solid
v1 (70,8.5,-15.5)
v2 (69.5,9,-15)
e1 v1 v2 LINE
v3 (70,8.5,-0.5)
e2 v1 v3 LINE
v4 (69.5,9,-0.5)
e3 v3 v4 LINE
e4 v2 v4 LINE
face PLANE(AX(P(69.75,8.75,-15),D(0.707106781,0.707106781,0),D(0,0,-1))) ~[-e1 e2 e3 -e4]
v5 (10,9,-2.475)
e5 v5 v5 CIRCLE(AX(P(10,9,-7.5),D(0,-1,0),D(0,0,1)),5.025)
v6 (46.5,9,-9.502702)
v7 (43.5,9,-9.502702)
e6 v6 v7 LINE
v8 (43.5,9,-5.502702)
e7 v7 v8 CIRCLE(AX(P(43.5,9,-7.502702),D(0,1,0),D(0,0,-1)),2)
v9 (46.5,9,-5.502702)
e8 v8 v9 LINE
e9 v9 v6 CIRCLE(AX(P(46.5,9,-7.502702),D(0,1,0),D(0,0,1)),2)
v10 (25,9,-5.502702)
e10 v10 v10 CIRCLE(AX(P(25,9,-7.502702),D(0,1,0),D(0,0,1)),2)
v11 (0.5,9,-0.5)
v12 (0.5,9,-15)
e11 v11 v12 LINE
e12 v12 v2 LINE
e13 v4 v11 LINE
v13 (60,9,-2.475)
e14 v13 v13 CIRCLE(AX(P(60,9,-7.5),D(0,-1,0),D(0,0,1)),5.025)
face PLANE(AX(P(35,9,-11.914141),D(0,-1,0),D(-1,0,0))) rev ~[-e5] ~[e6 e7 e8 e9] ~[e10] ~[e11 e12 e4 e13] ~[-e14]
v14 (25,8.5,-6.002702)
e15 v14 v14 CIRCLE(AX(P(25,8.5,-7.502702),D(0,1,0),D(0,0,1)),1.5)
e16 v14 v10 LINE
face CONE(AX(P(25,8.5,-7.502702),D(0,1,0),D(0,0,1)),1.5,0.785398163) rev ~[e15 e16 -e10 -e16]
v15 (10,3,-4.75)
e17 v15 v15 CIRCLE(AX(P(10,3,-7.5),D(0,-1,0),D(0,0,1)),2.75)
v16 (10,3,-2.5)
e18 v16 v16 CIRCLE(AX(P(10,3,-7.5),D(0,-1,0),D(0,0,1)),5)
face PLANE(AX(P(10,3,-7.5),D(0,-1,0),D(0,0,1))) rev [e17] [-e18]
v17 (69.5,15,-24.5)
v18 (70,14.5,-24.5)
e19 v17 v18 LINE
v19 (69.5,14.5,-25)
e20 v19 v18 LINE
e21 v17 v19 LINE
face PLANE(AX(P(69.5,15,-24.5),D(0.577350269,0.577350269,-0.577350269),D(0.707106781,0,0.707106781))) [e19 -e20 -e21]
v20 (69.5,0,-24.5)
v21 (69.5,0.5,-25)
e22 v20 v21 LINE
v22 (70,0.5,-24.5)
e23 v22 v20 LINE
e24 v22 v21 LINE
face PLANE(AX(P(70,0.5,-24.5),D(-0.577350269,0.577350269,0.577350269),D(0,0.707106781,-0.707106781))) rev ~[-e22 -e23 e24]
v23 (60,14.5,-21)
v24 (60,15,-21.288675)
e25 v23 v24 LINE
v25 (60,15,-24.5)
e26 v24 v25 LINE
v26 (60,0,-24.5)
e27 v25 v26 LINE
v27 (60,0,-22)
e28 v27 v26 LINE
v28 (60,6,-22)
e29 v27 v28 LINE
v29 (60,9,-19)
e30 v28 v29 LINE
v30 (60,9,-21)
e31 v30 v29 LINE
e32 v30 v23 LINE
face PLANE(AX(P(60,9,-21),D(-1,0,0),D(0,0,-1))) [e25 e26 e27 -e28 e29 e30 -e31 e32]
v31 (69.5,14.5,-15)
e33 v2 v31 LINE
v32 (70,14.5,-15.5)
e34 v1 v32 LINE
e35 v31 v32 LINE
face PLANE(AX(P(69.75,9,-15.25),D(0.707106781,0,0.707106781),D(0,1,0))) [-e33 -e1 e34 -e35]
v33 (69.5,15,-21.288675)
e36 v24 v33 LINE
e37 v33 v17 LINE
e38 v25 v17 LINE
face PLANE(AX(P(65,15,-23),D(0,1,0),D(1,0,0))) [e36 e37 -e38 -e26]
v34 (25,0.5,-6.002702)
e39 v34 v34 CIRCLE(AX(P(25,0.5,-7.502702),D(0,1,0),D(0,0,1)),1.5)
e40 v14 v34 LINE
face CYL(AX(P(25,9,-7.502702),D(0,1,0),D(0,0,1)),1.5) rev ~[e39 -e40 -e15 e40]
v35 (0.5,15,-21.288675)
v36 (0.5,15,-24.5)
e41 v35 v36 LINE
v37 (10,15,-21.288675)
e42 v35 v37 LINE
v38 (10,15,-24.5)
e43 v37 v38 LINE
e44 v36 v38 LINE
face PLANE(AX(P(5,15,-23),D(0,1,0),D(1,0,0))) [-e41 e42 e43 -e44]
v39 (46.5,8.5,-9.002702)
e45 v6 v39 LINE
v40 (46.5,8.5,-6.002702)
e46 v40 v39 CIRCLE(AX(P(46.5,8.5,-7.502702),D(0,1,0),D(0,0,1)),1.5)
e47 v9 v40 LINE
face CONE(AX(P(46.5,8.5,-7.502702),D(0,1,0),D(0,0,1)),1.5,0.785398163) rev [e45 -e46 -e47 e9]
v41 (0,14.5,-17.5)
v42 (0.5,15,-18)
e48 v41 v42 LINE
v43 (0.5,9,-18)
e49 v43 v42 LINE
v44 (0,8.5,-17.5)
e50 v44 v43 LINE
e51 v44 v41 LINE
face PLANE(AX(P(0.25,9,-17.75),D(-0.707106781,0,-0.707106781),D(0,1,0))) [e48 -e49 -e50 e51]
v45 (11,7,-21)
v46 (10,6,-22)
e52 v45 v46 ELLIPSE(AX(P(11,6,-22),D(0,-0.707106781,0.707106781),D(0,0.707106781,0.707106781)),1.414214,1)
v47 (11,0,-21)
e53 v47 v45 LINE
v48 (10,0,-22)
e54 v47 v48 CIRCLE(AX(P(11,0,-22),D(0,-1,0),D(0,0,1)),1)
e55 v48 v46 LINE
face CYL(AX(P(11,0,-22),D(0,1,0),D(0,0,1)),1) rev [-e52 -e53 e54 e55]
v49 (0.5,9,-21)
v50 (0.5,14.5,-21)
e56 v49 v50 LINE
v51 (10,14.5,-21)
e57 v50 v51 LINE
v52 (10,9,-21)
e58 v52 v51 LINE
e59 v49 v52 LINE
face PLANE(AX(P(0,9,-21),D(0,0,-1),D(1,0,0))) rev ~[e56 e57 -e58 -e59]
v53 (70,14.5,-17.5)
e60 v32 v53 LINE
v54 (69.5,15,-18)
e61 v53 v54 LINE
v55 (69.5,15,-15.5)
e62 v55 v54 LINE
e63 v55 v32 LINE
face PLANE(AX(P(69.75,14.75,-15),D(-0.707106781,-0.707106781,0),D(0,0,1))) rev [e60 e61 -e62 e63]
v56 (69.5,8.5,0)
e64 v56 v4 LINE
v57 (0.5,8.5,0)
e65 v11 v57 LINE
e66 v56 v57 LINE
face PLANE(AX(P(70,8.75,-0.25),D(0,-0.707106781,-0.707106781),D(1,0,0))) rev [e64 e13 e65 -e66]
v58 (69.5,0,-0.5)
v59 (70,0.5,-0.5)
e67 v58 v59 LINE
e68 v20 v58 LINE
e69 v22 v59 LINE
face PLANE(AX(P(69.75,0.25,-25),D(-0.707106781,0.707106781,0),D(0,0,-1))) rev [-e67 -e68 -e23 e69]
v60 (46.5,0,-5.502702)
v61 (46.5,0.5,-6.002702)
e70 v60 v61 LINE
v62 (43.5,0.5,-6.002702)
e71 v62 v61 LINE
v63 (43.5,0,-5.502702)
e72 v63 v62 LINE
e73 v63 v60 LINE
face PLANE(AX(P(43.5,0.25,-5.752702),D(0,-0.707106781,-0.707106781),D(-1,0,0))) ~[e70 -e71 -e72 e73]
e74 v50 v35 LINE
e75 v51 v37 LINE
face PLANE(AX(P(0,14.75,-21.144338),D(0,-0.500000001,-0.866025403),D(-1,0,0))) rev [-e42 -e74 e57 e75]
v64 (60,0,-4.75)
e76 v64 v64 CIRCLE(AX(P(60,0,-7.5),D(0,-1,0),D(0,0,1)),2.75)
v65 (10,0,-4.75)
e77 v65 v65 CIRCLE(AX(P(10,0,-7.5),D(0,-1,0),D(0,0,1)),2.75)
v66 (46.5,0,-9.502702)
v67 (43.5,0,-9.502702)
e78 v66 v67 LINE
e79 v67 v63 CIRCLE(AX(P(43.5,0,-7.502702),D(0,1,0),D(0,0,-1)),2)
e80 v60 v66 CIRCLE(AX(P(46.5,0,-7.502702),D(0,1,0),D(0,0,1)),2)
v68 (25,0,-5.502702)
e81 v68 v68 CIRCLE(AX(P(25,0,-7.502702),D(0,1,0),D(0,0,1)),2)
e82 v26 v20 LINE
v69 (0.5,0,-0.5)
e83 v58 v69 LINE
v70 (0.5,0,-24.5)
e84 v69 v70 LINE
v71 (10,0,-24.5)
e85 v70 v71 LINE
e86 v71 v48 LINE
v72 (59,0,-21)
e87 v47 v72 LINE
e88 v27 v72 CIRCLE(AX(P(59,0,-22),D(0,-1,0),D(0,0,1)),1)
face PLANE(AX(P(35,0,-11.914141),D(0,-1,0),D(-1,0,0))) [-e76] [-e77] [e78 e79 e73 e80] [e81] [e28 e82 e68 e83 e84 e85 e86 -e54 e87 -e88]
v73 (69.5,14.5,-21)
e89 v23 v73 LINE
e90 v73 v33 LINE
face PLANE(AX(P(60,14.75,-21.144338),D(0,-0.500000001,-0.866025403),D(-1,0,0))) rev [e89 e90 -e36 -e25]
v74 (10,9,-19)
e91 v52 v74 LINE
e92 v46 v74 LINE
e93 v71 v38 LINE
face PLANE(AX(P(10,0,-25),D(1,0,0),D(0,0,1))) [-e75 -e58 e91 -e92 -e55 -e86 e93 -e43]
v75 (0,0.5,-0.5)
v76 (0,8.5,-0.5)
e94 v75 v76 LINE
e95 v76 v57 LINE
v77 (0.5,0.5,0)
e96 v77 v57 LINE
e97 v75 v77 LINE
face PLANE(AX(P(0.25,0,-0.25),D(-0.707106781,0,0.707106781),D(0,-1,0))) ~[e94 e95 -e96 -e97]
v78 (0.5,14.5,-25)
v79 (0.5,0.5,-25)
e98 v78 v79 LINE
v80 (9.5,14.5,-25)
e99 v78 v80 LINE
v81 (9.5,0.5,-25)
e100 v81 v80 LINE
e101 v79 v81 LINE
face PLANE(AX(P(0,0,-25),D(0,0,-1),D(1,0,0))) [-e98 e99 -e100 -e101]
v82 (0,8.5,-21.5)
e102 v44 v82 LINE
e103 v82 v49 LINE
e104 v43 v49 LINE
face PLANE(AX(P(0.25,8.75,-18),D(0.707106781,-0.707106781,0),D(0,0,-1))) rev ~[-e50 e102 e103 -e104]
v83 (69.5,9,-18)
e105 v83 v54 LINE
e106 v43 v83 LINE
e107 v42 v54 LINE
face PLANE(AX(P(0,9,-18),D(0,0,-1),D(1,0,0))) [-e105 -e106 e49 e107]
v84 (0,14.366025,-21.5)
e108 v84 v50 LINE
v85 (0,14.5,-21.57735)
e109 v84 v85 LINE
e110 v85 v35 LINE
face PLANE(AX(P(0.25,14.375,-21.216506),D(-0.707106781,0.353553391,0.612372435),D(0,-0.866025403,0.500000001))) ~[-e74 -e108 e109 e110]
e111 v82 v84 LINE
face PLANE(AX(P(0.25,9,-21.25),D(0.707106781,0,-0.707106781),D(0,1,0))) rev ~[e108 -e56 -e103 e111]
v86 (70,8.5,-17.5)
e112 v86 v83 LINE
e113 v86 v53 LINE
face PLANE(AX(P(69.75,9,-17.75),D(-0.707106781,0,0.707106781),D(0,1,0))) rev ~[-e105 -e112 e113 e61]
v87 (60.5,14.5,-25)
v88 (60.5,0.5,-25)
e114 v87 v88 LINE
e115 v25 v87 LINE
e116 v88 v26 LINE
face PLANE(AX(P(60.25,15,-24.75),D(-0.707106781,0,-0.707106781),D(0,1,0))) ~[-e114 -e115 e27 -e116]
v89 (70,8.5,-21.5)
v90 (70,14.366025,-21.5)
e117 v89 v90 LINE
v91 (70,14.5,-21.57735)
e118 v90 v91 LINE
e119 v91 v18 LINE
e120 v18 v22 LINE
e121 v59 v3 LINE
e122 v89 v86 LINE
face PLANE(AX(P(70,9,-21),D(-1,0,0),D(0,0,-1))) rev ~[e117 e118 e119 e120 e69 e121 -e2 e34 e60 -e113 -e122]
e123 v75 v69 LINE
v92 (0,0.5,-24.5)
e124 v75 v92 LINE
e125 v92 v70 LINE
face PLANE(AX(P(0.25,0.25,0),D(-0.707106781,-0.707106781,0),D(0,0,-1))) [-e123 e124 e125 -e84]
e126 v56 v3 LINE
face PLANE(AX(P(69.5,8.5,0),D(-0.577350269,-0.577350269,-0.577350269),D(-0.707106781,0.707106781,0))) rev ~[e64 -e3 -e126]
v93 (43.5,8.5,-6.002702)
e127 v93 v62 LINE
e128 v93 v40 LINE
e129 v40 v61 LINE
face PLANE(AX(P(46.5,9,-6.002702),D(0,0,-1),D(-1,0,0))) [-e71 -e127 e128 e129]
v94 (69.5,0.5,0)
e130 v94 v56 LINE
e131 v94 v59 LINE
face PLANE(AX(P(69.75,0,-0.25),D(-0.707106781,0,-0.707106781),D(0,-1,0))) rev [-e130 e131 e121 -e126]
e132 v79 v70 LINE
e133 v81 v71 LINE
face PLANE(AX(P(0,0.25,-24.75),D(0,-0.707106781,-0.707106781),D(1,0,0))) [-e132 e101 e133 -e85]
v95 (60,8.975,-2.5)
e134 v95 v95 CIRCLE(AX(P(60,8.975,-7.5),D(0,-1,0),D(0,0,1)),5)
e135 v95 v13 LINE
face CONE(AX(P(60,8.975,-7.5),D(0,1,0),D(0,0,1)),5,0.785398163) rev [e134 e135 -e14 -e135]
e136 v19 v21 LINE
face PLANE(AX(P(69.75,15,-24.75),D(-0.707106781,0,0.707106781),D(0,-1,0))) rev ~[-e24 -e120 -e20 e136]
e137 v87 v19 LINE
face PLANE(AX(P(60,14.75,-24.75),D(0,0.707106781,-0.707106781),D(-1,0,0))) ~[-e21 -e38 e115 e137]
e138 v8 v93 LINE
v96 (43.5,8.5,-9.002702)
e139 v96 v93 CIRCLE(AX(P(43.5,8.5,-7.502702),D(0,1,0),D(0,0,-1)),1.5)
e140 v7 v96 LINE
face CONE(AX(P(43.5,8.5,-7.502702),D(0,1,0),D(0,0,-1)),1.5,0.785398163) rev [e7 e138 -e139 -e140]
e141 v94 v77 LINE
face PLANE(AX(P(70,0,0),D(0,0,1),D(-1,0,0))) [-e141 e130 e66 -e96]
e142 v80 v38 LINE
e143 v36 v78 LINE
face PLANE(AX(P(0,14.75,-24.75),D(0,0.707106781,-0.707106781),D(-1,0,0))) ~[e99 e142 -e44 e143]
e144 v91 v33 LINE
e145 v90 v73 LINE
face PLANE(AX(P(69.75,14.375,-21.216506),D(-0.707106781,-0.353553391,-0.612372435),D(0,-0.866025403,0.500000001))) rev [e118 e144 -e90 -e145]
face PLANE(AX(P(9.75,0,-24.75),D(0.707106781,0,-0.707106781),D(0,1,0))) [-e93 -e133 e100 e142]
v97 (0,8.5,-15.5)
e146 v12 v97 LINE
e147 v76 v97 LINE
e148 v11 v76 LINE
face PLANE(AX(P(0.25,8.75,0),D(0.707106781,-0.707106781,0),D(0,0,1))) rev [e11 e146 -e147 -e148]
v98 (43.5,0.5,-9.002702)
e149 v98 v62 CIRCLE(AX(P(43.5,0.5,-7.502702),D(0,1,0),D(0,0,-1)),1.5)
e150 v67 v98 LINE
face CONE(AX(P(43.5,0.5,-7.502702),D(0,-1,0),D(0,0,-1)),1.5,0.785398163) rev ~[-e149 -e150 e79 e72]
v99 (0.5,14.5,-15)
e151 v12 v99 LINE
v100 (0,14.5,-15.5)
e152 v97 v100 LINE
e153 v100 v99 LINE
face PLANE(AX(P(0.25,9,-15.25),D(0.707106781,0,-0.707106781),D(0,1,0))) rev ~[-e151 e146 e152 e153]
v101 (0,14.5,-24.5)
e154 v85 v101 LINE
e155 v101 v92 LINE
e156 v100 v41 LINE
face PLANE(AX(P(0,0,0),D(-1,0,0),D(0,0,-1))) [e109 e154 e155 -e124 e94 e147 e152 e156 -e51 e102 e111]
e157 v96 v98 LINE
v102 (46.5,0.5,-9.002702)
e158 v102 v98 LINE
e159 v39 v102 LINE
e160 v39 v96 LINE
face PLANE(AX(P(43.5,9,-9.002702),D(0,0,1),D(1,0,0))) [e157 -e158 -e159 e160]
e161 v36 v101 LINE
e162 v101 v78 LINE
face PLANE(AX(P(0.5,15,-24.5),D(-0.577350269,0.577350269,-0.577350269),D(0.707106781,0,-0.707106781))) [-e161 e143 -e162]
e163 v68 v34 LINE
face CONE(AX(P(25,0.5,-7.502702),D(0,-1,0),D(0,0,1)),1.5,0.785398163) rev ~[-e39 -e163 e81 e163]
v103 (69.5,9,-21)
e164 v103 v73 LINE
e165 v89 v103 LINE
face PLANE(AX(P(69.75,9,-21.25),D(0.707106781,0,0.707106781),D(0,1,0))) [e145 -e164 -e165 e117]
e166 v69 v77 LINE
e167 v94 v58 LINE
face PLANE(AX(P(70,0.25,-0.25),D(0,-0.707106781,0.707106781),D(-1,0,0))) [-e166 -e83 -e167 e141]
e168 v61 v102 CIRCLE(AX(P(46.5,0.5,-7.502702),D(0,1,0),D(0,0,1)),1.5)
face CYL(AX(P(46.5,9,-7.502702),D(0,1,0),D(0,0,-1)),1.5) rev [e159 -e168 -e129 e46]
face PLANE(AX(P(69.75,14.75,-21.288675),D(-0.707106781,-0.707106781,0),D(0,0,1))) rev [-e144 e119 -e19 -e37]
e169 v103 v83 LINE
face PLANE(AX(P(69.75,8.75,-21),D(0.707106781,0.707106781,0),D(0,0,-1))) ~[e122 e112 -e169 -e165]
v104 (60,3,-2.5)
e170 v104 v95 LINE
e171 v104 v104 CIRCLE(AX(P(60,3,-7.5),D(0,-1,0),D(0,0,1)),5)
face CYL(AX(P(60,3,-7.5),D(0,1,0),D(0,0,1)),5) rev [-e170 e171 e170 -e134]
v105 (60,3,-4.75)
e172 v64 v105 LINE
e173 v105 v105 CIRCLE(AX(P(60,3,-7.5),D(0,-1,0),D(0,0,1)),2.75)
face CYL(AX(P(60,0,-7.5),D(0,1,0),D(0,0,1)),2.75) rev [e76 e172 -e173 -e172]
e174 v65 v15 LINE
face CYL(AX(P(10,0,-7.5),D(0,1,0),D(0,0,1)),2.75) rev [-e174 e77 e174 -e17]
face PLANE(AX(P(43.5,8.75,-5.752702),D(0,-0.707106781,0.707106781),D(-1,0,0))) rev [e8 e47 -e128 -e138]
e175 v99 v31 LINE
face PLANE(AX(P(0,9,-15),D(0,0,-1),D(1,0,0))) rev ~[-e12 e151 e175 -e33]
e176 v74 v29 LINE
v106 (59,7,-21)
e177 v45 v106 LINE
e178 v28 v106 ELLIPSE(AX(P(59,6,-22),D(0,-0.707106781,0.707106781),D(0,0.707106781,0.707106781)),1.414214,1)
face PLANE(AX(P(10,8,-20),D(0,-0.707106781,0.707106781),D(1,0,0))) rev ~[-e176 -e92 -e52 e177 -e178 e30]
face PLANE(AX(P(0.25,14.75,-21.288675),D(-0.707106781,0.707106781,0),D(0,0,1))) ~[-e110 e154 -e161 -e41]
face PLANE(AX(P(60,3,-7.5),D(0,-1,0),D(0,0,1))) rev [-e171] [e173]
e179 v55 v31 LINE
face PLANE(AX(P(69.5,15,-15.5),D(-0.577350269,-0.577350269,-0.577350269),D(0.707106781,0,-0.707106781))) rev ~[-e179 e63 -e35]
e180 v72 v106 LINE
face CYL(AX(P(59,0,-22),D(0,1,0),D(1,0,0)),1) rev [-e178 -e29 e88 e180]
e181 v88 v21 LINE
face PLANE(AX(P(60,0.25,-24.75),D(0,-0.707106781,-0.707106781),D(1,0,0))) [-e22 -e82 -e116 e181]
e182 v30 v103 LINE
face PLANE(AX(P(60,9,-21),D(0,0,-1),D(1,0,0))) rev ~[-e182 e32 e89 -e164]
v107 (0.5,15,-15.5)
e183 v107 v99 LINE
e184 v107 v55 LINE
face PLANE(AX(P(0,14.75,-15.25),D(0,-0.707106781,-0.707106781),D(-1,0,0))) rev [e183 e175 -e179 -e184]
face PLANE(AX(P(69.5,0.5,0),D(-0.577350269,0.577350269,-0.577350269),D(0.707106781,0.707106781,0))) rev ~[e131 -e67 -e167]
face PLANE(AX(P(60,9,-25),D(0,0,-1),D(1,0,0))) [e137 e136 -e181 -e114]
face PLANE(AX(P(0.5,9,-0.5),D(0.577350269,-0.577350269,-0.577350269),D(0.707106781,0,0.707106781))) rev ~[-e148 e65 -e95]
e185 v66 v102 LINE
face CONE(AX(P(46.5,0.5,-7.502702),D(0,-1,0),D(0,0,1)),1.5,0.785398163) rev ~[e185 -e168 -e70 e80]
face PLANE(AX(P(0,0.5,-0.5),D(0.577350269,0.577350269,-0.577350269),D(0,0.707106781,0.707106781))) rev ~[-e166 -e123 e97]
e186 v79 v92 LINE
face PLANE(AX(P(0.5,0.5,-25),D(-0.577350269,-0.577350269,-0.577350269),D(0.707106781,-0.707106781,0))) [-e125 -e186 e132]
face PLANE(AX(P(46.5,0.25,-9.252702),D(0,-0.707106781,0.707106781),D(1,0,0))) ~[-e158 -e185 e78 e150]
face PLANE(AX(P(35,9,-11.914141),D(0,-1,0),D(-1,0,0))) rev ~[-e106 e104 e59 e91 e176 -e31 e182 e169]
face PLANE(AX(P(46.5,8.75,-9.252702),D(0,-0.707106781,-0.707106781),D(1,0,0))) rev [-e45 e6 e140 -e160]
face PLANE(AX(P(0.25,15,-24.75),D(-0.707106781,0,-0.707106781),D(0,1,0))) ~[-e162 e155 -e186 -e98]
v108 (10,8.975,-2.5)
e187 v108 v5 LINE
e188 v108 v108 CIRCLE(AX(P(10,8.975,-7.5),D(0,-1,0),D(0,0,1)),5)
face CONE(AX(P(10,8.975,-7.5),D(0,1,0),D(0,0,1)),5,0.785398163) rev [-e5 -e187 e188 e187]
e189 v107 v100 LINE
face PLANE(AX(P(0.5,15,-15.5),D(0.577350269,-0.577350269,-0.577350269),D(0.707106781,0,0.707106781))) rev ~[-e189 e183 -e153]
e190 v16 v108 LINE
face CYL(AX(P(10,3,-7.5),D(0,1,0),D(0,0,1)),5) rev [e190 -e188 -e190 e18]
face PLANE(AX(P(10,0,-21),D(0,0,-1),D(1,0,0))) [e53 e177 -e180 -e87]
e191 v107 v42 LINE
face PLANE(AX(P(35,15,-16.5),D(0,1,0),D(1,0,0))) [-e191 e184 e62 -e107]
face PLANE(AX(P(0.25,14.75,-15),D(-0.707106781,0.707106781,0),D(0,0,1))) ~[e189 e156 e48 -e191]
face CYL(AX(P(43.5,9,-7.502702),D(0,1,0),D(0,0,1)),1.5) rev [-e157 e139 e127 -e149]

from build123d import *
from OCP.BRepFilletAPI import BRepFilletAPI_MakeChamfer

# Parameters (mm, degrees)
BOSS_EXTRUDE1_DEPTH                          = 9
SKETCH2_W                                    = 70
SKETCH2_H                                    = 3
SKETCH2_W_2                                  = 10
SKETCH2_H_2                                  = 4
BOSS_EXTRUDE2_DEPTH                          = 6
CBORE_FOR_M5_SLOTTED_CHEESE_HEAD_SCR_2_COUNT = 2
CBORE_FOR_M5_SLOTTED_CHEESE_HEAD_SCR_2_PITCH = 50
SKETCH13_R                                   = 1.5
CUT_EXTRUDE1_DEPTH                           = 75.873226189
CHAMFER3_SIZE                                = 0.5
CHAMFER3_SIZE2                               = 0.288675135
CHAMFER9_SIZE                                = 2
FILLET1_R                                    = 1
CHAMFER6_SIZE                                = 0.5
CHAMFER7_SIZE                                = 0.5
CUT_EXTRUDE2_DEPTH                           = 75.873226189
CHAMFER8_SIZE                                = 0.5


with BuildPart() as part:
    # Sketch1 → Boss-Extrude1 (new body)
    with BuildSketch(Plane(origin=(0, 0, 0), x_dir=(1, 0, 0), z_dir=(0, 1, 0))):
        Polygon((10, 21), (60, 21), (60, 25), (70, 25), (70, 0), (0, 0), (0, 25), (10, 25), align=None)
    extrude(amount=BOSS_EXTRUDE1_DEPTH)

    # Sketch2 → Boss-Extrude2 (add)
    with BuildSketch(Plane(origin=(0, 9, 0), x_dir=(1, 0, 0), z_dir=(0, 1, 0))):
        with Locations((35, 16.5)):
            Rectangle(SKETCH2_W, SKETCH2_H)
        with Locations((65, 23)):
            Rectangle(SKETCH2_W_2, SKETCH2_H_2)
        with Locations((5, 23)):
            Rectangle(SKETCH2_W_2, SKETCH2_H_2)
    extrude(amount=BOSS_EXTRUDE2_DEPTH)

    # Sketch12 → CBORE for M5 Slotted cheese head screws1 (revolve, cut)
    with BuildSketch(Plane(origin=(10, 9, -7.5), x_dir=(0, 0, 1), z_dir=(1, 0, 0))):
        Polygon((0, 0), (0, 9), (2.75, 9), (2.75, 6), (5, 6), (5, 0.025), (5.025, 0), align=None)
    cbore_for_m5_slotted_cheese_head_screws1 = revolve(axis=Axis((10, 15.35, -7.5), (0, -1, 0)), mode=Mode.SUBTRACT)

    # CBORE for M5 Slotted cheese head scr 2: CBORE for M5 Slotted cheese head screws1 ×2
    with Locations(*[(i * CBORE_FOR_M5_SLOTTED_CHEESE_HEAD_SCR_2_PITCH, 0, 0) for i in range(1, CBORE_FOR_M5_SLOTTED_CHEESE_HEAD_SCR_2_COUNT)]):
        add(cbore_for_m5_slotted_cheese_head_screws1, mode=Mode.SUBTRACT)

    # Sketch13 → Cut-Extrude1 (cut, through all)
    with BuildSketch(Plane(origin=(0, 9, 0), x_dir=(1, 0, 0), z_dir=(0, 1, 0))):
        with Locations(Location((45.000000243, 7.502702464, 0), (0, 0, 270))):
            Circle(SKETCH13_R)
        with Locations(Location((25.000000243, 7.502702464, 0), (0, 0, 270))):
            Circle(SKETCH13_R)
    extrude(amount=-CUT_EXTRUDE1_DEPTH, mode=Mode.SUBTRACT)

    # Chamfer3: one chamfer whose edges measure the first distance from different faces: ONE call of the kernel's chamfer builder (chamfer() names one face for all edges)
    chamfer3_edges_1 = [part.edges().sort_by_distance(p)[0] for p in [
        (5, 15, -21),
    ]]
    chamfer3_side_1 = [part.faces().sort_by_distance(p)[0] for p in [
        (5, 12, -21),
    ]]
    chamfer3_edges_2 = [part.edges().sort_by_distance(p)[0] for p in [
        (65, 15, -21),
    ]]
    chamfer3_side_2 = [part.faces().sort_by_distance(p)[0] for p in [
        (65, 12, -21),
    ]]
    chamfer3 = BRepFilletAPI_MakeChamfer(part.part.solid().wrapped)
    for e in chamfer3_edges_1:
        chamfer3.Add(CHAMFER3_SIZE, CHAMFER3_SIZE2, e.wrapped, chamfer3_side_1[0].wrapped)  # the first distance lies on this face
    for e in chamfer3_edges_2:
        chamfer3.Add(CHAMFER3_SIZE, CHAMFER3_SIZE2, e.wrapped, chamfer3_side_2[0].wrapped)  # the first distance lies on this face
    add(Compound.cast(chamfer3.Shape()), mode=Mode.REPLACE)

    # Chamfer9
    chamfer9_edges = [part.edges().sort_by_distance(p)[0] for p in [
        (35, 9, -21),
    ]]
    chamfer(chamfer9_edges, length=CHAMFER9_SIZE)

    # Fillet1
    fillet1_edges = [part.edges().sort_by_distance(p)[0] for p in [
        (10, 3.5, -21),
        (60, 3.5, -21),
    ]]
    fillet(fillet1_edges, radius=FILLET1_R)

    # Chamfer6
    chamfer6_edges = [part.edges().sort_by_distance(p)[0] for p in [
        (65, 0, -25),
        (70, 0, -12.5),
        (35, 0, 0),
        (0, 0, -12.5),
        (70, 9, -7.5),
        (0, 7.5, -25),
        (10, 7.5, -25),
        (60, 7.5, -25),
        (70, 7.5, -25),
        (70, 4.5, 0),
        (0, 4.5, 0),
        (0, 9, -7.5),
        (70, 9, -19.5),
        (0, 12, -18),
        (0, 12, -15),
        (70, 12, -15),
        (70, 12, -18),
        (0, 15, -16.5),
        (35, 15, -15),
        (70, 15, -16.5),
        (0, 9, -19.5),
        (0, 15, -23.144337567),
        (5, 15, -25),
        (65, 15, -25),
        (5, 0, -25),
        (70, 15, -23.144337567),
        (35, 9, 0),
        (70, 11.75, -21),
        (70, 14.75, -21.144337567),
        (0, 11.75, -21),
        (0, 14.75, -21.144337567),
    ]]
    chamfer(chamfer6_edges, length=CHAMFER6_SIZE)

    # Chamfer7
    chamfer7_edges = [part.edges().sort_by_distance(p)[0] for p in [
        (25.000000243, 0, -9.002702464),
        (25.000000243, 9, -9.002702464),
    ]]
    chamfer(chamfer7_edges, length=CHAMFER7_SIZE)

    # Sketch14 → Cut-Extrude2 (cut, through all)
    with BuildSketch(Plane(origin=(0, 9, 0), x_dir=(1, 0, 0), z_dir=(0, 1, 0))):
        with BuildLine():
            Line((43.500000243, 9.002702464), (46.500000243, 9.002702464))
            ThreePointArc((46.500000243, 9.002702464), (48.000000243, 7.502702464), (46.500000243, 6.002702464))
            Line((46.500000243, 6.002702464), (43.500000243, 6.002702464))
            ThreePointArc((43.500000243, 6.002702464), (42.000000243, 7.502702464), (43.500000243, 9.002702464))
        make_face()
    extrude(amount=-CUT_EXTRUDE2_DEPTH, mode=Mode.SUBTRACT)

    # Chamfer8
    chamfer8_edges = [part.edges().sort_by_distance(p)[0] for p in [
        (45.000000243, 0, -9.002702464),
        (45.000000243, 0, -6.002702464),
        (45.000000243, 9, -6.002702464),
        (45.000000243, 9, -9.002702464),
        (42.000000243, 9, -7.502702464),
        (48.000000243, 9, -7.502702464),
        (42.000000243, 0, -7.502702464),
        (48.000000243, 0, -7.502702464),
    ]]
    chamfer(chamfer8_edges, length=CHAMFER8_SIZE)


solid = part.part
